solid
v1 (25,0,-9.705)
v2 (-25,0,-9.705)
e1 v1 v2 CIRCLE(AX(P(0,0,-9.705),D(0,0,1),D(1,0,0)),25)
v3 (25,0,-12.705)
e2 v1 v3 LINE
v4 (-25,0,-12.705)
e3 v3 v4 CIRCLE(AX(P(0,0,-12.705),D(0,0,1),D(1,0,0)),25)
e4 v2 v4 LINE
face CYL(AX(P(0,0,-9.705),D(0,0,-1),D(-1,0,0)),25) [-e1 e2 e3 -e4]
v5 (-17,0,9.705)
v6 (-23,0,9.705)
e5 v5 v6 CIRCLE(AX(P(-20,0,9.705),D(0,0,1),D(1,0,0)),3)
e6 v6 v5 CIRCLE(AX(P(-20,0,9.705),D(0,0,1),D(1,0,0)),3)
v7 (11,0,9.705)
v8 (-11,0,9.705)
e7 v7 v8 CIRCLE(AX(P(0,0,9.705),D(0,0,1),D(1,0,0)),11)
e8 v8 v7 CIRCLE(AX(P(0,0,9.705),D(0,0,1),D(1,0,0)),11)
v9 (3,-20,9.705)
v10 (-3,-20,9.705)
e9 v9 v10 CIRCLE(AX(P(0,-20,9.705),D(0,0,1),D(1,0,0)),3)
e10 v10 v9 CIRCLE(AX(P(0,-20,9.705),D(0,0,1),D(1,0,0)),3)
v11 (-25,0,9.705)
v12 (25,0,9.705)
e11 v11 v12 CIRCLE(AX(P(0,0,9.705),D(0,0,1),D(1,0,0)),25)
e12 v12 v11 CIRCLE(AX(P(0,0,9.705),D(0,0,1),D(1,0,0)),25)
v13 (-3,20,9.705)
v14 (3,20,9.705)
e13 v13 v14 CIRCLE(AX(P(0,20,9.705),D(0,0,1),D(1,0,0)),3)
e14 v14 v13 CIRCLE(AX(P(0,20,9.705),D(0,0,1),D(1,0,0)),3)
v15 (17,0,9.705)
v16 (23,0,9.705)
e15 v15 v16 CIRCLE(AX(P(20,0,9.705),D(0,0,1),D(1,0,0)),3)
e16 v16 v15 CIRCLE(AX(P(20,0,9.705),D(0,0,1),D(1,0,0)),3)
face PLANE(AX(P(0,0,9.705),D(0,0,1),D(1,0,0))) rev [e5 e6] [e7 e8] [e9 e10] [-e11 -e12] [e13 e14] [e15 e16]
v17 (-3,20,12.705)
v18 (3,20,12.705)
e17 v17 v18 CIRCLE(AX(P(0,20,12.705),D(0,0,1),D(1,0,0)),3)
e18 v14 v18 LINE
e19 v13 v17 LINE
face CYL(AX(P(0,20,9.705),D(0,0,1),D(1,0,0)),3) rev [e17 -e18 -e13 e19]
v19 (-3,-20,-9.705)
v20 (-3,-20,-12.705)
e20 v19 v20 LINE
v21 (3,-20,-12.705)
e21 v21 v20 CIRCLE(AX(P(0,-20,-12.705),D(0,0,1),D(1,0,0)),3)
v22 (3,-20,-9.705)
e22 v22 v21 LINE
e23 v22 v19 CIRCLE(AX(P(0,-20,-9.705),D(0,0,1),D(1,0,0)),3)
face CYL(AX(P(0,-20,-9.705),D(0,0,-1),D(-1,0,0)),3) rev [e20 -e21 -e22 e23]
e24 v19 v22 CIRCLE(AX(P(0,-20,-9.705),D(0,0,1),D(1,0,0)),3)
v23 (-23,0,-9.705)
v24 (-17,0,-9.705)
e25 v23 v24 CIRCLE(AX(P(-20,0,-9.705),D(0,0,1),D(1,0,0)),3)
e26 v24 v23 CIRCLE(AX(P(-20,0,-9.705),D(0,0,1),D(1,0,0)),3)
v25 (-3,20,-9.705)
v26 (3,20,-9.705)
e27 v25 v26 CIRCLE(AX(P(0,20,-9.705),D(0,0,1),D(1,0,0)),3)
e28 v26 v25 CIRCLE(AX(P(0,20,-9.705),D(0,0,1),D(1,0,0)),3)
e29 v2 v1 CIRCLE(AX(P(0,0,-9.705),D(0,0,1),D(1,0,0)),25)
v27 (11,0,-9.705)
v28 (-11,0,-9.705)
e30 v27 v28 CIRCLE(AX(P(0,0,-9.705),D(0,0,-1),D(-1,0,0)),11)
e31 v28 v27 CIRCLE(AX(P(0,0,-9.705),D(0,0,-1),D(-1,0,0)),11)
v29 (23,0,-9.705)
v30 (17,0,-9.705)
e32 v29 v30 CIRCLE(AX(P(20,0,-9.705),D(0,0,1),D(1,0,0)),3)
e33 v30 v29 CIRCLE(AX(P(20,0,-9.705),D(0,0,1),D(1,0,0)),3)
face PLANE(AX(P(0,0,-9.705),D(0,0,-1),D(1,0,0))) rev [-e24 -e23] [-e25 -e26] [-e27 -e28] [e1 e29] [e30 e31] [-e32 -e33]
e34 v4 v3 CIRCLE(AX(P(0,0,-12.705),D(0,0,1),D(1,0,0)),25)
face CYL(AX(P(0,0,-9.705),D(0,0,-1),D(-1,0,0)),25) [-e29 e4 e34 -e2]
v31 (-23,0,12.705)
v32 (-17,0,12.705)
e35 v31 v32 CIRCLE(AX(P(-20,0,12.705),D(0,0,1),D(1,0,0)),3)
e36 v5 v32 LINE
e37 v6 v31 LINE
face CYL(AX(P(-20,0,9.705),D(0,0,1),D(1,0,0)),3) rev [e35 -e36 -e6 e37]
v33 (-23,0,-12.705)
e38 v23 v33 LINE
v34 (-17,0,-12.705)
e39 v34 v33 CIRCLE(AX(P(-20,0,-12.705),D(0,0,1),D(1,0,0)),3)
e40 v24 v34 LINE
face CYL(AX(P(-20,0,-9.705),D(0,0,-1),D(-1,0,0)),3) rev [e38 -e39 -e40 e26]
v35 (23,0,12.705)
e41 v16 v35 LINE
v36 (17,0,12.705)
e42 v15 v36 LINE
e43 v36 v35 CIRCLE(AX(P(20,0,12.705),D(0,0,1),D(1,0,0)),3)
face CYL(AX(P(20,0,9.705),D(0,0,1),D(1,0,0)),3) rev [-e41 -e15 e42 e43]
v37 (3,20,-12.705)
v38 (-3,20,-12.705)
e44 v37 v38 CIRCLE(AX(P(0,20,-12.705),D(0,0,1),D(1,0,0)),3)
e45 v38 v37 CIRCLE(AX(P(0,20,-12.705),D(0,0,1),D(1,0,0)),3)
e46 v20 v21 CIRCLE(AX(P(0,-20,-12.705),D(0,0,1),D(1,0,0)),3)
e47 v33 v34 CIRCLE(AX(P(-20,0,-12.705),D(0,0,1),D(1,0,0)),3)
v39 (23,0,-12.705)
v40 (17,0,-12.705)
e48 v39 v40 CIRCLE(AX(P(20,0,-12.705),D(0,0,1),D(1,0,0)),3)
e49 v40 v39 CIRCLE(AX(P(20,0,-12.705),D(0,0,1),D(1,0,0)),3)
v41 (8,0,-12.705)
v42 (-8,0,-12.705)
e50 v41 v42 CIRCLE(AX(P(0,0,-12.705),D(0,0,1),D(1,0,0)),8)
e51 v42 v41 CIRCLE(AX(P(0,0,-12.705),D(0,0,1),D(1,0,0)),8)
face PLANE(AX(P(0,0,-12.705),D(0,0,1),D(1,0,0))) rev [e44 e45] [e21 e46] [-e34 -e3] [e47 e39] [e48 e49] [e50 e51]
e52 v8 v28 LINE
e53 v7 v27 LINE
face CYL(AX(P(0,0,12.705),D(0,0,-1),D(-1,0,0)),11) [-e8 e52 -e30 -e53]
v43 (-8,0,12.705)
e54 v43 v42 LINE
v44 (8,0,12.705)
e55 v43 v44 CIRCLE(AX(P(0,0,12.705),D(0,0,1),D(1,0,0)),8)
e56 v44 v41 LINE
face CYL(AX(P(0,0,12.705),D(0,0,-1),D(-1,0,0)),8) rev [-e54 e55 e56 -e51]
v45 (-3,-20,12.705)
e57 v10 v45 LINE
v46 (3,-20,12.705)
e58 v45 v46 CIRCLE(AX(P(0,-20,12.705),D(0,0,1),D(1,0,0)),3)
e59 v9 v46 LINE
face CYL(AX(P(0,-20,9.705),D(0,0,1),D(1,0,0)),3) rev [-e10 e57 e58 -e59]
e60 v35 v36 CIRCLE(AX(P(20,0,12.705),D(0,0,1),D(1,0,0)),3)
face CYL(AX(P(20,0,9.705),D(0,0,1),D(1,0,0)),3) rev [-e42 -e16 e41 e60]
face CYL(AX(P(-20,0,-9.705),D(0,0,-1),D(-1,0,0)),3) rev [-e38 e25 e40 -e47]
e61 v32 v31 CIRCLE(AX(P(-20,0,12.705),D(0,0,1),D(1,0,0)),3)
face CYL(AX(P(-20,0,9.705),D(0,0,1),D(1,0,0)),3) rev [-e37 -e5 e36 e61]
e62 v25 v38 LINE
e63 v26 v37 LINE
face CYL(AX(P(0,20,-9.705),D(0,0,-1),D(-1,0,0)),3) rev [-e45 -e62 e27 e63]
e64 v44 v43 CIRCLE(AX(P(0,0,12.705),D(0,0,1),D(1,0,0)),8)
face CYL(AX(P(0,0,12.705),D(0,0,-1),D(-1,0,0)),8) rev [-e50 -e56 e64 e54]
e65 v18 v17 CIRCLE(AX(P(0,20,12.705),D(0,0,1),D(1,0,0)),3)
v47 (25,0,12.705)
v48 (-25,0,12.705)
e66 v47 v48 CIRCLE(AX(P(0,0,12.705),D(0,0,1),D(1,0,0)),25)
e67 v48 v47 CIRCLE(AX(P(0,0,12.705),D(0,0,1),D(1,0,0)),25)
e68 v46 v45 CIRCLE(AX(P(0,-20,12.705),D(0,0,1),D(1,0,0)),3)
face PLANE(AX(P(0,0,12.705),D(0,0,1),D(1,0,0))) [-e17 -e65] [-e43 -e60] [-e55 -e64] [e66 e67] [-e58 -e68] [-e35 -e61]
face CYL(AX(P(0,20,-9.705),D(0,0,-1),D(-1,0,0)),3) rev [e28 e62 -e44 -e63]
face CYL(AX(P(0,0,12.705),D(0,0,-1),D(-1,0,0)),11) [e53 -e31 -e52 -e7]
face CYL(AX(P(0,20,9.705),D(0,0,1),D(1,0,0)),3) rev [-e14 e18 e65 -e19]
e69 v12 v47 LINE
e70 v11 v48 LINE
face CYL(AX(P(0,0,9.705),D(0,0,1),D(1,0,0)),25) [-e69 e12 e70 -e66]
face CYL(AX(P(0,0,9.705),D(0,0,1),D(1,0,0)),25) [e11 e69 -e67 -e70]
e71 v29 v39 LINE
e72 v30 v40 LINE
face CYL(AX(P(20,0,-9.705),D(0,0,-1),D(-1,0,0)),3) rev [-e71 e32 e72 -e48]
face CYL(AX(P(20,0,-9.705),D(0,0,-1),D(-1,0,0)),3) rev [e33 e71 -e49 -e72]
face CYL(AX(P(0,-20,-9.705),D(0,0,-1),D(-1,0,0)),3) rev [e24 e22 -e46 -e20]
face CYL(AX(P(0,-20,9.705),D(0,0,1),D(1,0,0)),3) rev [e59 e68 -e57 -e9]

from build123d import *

# Parameters (mm, degrees)
SKETCH_1_R        = 11
SKETCH_1_R_2      = 8
EXTRUDE_1_DEPTH   = 12.705
EXTRUDE_START     = -3
SKETCH_2_R        = 25
SKETCH_2_R_2      = 8
SKETCH_2_R_3      = 3
EXTRUDE_1_2_DEPTH = 3


with BuildPart() as part:
    # 草图1 → Extrude 1 (new, symmetric)
    with BuildSketch(Plane.XY):
        Circle(SKETCH_1_R)
        Circle(SKETCH_1_R_2, mode=Mode.SUBTRACT)
    extrude(amount=EXTRUDE_1_DEPTH, both=True)

    # 草图2 → Extrude 1 2 (add)
    with BuildSketch(Plane.XY.offset(12.705).offset(EXTRUDE_START)):
        Circle(SKETCH_2_R)
        Circle(SKETCH_2_R_2, mode=Mode.SUBTRACT)
        with Locations((0, 20)):
            Circle(SKETCH_2_R_3, mode=Mode.SUBTRACT)
        with Locations((20, 0)):
            Circle(SKETCH_2_R_3, mode=Mode.SUBTRACT)
        with Locations((0, -20)):
            Circle(SKETCH_2_R_3, mode=Mode.SUBTRACT)
        with Locations((-20, 0)):
            Circle(SKETCH_2_R_3, mode=Mode.SUBTRACT)
    extrude_1_2 = extrude(amount=EXTRUDE_1_2_DEPTH)

    # 镜向1: Extrude 1 2 across plane
    add(extrude_1_2.mirror(Plane.XY))


solid = part.part
